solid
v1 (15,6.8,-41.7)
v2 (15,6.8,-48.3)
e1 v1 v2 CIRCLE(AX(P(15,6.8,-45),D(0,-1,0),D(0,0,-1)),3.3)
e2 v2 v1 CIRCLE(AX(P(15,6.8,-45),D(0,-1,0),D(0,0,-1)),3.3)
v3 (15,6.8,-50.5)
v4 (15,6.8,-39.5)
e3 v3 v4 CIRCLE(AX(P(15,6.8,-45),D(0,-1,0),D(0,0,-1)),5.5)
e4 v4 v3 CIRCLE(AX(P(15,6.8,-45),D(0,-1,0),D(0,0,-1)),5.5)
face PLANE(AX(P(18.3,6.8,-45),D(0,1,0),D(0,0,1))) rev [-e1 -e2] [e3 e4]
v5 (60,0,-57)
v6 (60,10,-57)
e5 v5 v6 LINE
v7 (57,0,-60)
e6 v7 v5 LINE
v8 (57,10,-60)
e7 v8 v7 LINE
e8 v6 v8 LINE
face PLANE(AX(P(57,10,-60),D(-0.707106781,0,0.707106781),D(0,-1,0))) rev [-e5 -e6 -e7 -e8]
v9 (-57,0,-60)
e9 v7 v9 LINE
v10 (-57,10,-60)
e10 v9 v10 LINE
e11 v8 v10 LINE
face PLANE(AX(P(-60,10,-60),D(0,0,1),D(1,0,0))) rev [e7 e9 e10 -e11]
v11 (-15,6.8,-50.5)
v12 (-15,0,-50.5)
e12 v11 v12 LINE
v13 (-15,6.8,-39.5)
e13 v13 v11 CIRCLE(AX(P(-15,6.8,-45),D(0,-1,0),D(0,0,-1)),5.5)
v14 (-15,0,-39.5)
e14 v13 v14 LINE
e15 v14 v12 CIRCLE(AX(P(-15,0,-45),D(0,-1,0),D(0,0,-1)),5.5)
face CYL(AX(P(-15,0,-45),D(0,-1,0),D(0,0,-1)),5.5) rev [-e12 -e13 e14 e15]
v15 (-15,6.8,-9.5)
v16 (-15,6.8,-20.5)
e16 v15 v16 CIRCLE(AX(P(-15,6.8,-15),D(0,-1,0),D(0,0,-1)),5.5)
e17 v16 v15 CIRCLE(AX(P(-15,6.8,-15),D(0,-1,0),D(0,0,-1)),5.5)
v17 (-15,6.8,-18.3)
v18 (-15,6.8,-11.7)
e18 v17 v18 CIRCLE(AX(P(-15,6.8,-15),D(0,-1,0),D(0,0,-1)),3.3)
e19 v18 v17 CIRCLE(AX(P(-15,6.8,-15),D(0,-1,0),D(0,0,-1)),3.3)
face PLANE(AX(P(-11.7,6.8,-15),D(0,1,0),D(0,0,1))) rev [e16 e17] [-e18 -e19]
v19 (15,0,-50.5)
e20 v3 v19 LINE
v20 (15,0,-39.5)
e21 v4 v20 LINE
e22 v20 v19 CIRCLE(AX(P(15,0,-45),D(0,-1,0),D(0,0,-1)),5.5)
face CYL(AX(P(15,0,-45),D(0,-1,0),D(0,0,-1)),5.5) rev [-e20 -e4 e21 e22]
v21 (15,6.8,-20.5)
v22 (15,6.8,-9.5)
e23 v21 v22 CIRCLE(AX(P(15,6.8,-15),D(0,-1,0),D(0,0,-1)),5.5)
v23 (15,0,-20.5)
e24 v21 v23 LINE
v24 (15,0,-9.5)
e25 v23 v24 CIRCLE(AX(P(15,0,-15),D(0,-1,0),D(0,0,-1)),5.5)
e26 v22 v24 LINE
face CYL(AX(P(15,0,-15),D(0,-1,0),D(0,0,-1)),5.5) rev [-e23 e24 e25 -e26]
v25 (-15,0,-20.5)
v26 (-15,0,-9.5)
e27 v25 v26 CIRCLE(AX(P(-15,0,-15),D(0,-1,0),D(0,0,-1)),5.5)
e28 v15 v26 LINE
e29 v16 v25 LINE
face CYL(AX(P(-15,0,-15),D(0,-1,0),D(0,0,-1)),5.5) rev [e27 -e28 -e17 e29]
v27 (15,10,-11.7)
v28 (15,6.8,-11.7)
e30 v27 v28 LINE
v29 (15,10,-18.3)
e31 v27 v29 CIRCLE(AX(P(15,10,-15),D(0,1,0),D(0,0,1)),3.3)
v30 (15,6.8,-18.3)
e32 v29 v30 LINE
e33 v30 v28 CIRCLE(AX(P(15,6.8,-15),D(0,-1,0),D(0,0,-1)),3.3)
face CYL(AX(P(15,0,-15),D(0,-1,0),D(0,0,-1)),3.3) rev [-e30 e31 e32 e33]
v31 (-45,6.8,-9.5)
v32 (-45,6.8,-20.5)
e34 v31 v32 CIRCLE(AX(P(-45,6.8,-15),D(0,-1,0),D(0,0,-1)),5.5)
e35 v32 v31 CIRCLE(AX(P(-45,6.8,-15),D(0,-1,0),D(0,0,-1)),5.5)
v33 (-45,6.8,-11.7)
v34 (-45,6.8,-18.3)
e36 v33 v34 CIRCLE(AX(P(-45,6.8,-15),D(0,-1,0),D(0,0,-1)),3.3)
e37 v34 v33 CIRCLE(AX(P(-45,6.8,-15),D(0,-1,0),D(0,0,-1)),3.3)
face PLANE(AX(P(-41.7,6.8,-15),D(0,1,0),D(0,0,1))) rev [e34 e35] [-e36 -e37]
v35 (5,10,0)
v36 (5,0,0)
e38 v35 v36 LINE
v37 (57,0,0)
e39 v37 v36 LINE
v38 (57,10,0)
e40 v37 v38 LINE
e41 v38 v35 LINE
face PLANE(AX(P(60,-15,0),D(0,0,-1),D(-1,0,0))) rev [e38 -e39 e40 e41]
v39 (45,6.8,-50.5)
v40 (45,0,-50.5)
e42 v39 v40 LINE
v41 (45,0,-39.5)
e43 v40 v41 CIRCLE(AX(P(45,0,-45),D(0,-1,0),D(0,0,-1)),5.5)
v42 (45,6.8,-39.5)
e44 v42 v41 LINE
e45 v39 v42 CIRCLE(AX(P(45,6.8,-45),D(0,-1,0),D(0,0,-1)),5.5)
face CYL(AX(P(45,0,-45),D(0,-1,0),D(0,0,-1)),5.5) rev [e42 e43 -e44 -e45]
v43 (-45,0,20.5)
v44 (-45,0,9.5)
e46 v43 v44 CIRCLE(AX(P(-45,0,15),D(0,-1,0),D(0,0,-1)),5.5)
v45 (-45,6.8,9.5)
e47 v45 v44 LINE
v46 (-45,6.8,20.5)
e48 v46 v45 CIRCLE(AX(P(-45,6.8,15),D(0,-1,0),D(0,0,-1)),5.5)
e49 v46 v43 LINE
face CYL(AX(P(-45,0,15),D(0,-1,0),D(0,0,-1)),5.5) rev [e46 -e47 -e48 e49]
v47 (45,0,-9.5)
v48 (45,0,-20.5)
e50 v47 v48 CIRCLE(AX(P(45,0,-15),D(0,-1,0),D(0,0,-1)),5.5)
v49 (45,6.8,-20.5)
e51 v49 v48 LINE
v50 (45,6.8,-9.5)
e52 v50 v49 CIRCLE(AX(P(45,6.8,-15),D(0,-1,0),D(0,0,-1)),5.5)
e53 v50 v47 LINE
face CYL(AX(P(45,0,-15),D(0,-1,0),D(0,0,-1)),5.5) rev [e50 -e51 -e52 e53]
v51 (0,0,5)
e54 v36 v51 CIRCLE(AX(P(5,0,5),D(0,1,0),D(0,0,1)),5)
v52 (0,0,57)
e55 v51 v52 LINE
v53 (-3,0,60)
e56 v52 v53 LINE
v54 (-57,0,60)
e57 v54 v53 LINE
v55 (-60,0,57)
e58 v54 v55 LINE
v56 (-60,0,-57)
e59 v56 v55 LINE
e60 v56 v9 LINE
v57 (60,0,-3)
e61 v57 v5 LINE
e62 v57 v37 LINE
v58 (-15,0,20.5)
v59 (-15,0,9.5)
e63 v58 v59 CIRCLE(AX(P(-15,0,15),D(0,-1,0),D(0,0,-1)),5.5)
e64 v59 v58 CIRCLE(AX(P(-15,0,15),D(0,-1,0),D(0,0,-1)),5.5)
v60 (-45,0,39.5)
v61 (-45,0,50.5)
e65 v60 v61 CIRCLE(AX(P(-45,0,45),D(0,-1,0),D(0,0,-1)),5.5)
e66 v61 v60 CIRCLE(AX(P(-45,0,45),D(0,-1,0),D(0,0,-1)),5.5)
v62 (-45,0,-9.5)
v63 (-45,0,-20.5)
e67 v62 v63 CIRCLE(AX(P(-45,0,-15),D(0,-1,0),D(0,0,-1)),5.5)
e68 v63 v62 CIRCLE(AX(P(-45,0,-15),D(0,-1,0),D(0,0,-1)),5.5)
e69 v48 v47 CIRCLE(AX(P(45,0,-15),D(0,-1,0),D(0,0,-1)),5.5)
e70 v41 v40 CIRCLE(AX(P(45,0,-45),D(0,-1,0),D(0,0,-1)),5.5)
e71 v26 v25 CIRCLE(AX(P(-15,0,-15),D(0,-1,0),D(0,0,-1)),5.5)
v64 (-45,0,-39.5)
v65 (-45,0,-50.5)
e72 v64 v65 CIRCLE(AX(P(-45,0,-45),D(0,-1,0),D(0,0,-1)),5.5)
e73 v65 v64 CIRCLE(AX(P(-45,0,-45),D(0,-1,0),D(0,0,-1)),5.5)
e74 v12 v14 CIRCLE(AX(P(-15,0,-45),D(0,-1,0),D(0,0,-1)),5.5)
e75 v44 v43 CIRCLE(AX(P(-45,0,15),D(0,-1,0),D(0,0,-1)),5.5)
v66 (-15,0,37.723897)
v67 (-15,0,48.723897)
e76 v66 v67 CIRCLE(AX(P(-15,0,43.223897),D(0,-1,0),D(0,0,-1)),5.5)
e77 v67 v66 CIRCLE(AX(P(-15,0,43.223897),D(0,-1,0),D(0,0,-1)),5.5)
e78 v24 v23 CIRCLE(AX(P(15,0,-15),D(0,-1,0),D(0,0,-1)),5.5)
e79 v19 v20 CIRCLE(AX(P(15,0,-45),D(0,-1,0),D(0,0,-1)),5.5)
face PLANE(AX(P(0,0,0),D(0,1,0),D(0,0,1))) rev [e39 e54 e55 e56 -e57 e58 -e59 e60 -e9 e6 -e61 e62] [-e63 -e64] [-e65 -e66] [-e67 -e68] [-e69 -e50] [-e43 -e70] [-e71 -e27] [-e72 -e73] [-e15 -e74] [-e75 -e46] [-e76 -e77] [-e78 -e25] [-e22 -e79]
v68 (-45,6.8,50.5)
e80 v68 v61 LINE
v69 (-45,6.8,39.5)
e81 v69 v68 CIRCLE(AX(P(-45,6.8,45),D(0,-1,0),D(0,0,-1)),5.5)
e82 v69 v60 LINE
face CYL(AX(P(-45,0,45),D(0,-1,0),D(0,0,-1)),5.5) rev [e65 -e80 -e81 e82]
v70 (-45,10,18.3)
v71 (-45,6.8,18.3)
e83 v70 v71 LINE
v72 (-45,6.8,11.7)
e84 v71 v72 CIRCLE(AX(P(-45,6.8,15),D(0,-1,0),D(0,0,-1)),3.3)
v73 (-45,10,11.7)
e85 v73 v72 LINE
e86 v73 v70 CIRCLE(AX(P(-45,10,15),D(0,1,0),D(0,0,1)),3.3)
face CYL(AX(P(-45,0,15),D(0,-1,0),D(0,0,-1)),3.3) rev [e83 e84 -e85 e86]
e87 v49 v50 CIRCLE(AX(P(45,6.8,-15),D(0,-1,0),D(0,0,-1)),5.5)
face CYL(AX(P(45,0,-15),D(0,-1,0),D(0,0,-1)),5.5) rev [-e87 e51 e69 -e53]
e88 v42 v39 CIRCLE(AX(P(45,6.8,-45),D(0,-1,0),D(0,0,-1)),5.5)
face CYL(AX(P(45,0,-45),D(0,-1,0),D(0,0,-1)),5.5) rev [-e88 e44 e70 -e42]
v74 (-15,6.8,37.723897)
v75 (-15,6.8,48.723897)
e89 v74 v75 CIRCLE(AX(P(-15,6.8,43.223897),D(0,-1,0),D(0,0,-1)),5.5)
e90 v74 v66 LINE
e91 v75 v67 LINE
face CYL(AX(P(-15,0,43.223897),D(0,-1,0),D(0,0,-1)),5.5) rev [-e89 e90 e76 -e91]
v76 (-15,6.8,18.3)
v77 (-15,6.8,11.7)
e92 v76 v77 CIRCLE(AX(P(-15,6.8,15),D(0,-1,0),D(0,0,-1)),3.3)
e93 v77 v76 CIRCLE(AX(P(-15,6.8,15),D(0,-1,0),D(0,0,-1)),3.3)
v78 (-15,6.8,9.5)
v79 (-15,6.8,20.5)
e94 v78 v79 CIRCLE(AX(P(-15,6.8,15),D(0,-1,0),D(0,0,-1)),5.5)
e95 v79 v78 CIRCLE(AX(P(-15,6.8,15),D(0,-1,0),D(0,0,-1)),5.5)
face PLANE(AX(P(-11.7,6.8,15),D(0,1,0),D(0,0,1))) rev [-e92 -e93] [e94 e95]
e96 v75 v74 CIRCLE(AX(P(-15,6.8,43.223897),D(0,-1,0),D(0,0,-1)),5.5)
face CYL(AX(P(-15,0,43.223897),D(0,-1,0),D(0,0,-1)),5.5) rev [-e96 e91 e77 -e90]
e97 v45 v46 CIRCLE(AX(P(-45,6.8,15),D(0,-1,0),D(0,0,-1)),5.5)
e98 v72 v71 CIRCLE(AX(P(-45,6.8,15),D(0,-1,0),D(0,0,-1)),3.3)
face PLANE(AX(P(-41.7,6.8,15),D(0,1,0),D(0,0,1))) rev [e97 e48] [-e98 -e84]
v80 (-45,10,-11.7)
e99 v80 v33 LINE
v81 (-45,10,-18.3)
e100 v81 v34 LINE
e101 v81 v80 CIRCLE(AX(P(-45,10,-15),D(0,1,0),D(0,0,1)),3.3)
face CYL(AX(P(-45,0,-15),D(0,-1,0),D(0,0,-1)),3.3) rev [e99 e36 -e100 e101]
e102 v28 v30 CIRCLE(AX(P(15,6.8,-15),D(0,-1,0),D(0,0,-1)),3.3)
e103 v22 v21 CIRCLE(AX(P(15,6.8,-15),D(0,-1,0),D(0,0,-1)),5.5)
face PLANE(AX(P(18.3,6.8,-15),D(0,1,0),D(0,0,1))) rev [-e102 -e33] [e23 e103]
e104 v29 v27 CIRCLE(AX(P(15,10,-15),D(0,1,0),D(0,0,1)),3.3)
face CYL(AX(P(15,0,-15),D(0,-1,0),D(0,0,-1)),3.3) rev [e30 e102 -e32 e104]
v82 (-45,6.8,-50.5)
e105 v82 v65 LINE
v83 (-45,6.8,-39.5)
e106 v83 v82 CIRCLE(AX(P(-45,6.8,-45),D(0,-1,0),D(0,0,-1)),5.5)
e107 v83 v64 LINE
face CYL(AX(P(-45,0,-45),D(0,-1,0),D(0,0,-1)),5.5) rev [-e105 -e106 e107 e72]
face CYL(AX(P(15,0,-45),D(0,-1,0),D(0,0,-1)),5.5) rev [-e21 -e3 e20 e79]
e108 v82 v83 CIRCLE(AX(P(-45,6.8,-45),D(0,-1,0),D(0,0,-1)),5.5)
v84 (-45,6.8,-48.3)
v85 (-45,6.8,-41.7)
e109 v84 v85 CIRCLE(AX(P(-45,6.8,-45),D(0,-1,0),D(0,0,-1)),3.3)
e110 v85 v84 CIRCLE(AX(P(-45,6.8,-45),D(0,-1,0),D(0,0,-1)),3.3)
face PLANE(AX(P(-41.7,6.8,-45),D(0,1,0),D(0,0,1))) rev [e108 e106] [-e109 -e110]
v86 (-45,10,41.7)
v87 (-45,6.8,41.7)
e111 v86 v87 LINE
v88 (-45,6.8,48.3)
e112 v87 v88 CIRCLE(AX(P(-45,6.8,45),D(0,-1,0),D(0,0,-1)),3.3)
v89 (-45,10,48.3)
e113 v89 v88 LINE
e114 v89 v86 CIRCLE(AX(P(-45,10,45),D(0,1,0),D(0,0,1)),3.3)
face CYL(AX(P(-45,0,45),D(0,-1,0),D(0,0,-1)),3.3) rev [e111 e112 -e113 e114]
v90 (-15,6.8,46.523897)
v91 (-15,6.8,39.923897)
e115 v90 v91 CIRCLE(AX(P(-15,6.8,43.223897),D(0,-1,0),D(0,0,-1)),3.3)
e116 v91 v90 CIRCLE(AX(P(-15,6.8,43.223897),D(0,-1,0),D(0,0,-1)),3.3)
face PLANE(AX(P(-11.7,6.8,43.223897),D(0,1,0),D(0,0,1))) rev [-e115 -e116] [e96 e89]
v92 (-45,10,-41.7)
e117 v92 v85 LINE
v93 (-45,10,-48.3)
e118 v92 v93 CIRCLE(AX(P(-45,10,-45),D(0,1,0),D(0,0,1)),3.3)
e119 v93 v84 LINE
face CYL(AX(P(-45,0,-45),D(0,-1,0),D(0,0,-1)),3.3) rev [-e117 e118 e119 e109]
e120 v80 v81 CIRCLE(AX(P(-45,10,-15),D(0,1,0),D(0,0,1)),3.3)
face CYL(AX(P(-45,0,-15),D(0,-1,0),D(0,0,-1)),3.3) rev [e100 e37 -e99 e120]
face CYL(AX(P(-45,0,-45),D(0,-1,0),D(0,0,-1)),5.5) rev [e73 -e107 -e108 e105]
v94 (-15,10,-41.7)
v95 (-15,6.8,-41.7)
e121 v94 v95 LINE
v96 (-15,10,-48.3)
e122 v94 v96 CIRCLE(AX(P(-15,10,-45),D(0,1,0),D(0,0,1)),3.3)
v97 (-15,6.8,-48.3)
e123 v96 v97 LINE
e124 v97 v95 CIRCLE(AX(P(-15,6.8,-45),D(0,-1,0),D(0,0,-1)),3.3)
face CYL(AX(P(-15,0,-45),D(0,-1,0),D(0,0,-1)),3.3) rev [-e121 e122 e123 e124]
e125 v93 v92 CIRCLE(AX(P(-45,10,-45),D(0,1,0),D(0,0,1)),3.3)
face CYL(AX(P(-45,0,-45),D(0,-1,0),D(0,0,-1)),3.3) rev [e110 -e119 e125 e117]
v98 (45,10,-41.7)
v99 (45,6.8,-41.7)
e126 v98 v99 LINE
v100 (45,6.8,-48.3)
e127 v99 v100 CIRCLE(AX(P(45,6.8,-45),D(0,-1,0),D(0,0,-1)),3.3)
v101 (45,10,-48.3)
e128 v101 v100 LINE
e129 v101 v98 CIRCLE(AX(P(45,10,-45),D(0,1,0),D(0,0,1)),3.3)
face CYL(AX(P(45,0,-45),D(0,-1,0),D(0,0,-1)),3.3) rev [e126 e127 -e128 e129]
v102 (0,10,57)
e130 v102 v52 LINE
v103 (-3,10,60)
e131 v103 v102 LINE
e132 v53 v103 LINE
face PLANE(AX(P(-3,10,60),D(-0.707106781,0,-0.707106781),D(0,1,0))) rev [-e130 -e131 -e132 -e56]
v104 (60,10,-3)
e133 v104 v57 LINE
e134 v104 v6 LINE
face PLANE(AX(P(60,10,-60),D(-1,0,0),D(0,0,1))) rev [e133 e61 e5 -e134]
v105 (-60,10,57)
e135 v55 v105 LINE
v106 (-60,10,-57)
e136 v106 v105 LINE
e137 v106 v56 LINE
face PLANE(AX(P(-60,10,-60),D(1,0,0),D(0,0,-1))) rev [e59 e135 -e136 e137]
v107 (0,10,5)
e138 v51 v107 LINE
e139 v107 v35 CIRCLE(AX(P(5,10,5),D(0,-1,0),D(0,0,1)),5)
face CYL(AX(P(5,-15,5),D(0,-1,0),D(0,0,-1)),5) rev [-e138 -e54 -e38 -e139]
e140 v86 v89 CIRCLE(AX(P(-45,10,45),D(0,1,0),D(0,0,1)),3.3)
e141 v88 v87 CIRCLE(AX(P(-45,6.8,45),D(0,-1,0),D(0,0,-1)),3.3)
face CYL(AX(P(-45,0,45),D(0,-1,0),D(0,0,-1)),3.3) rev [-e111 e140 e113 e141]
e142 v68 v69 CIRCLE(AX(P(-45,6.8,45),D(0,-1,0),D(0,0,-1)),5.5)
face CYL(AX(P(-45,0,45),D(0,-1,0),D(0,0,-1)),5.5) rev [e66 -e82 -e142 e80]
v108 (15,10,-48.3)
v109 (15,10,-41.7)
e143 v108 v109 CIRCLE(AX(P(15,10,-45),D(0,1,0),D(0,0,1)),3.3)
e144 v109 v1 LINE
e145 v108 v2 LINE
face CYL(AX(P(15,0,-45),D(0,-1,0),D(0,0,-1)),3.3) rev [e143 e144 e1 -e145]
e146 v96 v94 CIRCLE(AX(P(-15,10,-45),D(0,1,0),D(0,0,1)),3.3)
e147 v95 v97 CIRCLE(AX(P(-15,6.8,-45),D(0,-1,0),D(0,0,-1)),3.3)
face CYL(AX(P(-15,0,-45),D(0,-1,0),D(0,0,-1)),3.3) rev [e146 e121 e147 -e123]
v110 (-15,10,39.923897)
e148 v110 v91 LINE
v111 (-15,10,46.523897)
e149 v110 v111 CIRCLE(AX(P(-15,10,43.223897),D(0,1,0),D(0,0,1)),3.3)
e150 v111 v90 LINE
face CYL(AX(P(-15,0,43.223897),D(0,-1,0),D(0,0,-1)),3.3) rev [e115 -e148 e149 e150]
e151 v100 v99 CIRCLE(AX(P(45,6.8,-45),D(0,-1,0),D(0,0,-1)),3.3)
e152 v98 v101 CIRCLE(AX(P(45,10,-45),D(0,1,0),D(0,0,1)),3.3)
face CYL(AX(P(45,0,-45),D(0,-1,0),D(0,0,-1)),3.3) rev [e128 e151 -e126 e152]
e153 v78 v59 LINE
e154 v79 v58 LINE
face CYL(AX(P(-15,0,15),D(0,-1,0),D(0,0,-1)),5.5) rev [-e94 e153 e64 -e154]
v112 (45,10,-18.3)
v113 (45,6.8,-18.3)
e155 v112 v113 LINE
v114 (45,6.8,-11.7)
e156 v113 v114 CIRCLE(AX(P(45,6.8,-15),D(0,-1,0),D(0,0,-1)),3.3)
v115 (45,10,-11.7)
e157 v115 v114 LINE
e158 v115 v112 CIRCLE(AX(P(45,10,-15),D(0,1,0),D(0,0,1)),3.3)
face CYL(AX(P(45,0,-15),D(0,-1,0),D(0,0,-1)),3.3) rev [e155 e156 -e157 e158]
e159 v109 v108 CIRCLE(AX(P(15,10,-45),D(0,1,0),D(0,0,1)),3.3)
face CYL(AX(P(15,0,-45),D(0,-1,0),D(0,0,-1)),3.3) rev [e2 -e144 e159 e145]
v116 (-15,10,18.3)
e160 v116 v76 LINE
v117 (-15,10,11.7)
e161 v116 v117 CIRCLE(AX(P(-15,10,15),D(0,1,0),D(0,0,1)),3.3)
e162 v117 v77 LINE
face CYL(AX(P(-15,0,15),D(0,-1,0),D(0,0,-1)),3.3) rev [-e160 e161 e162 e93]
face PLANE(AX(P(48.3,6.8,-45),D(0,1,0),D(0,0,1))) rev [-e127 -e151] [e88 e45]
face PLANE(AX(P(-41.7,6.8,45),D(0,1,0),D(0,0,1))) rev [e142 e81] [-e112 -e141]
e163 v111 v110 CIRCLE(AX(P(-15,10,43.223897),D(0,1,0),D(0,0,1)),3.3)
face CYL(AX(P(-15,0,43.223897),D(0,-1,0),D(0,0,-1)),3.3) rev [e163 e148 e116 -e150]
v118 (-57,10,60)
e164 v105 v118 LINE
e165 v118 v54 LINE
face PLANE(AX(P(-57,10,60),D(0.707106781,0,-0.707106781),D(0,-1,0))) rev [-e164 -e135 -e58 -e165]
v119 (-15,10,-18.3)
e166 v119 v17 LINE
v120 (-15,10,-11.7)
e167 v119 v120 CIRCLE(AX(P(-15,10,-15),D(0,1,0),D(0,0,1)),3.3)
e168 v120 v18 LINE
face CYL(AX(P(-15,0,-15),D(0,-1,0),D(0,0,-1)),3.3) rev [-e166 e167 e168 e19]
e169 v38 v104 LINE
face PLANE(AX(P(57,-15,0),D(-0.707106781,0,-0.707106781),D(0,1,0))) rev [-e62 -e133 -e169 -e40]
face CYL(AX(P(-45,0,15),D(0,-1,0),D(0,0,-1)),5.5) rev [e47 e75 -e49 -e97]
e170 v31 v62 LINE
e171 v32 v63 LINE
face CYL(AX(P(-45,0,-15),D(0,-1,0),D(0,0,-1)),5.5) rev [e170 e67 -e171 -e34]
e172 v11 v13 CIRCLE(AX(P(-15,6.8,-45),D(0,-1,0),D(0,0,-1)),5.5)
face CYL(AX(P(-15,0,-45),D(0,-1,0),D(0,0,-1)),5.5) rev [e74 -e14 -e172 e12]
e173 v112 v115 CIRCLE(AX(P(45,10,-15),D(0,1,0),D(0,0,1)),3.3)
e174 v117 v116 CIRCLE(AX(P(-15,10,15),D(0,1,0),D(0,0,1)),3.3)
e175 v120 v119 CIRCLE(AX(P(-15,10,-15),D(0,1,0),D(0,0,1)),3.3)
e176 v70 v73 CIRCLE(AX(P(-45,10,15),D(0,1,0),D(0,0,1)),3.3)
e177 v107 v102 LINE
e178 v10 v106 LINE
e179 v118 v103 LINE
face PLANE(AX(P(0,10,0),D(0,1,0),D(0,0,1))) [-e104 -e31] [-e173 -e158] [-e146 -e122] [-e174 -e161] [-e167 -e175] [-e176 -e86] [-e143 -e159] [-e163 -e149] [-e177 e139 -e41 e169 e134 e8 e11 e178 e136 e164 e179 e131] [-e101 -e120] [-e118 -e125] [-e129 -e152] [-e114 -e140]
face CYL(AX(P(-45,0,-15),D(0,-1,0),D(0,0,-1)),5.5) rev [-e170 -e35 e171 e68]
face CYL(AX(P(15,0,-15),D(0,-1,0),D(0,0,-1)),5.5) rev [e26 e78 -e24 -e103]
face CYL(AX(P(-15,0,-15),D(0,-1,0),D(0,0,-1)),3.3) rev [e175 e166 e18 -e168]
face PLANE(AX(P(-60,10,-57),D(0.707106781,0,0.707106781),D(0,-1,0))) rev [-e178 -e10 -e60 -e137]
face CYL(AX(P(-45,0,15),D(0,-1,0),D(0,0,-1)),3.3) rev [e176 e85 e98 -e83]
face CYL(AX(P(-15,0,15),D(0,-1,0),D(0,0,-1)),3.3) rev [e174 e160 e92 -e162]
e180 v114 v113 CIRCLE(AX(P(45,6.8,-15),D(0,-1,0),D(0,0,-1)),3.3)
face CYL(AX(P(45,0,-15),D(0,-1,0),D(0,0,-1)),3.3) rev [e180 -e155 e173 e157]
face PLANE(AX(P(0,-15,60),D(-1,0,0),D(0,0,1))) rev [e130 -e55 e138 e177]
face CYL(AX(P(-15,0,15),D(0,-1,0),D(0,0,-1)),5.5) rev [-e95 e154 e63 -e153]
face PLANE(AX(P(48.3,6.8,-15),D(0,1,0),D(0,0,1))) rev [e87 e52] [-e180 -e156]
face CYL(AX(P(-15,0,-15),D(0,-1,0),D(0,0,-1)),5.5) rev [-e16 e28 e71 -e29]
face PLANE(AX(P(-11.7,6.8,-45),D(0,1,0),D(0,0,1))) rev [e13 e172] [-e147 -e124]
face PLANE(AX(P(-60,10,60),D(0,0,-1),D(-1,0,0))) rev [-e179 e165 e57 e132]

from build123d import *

# Parameters (mm, degrees)
SKETCH_1_W                = 120
SKETCH_1_H                = 120
EXTRUDE_1_DEPTH           = 10
SKETCH_2_W                = 60
SKETCH_2_H                = 60
CUT_EXTRUDE_1_DEPTH       = 25
CHAMFER_1_SIZE            = 3
FILLET_1_R                = 5
HOLE_WIZARD_1_D           = 6.6
HOLE_WIZARD_1_DEPTH       = 25
HOLE_WIZARD_1_CBORE_D     = 11
HOLE_WIZARD_1_CBORE_DEPTH = 6.8
HOLE_WIZARD_1_TIP         = 1.982840043


with BuildPart() as part:
    # 草图1 → 凸台-拉伸1 (new body)
    with BuildSketch(Plane(origin=(0, 0, 0), x_dir=(1, 0, 0), z_dir=(0, 1, 0))):
        Rectangle(SKETCH_1_W, SKETCH_1_H)
    extrude(amount=EXTRUDE_1_DEPTH)

    # 草图2 → 切除-拉伸1 (cut)
    with BuildSketch(Plane(origin=(0, 10, 0), x_dir=(1, 0, 0), z_dir=(0, 1, 0))):
        with Locations((30, -30)):
            Rectangle(SKETCH_2_W, SKETCH_2_H)
    extrude(amount=-CUT_EXTRUDE_1_DEPTH, mode=Mode.SUBTRACT)

    # 倒角1
    chamfer_1_edges = [part.edges().sort_by_distance(p)[0] for p in [
        (60, 5, 0),
        (0, 5, 60),
        (-60, 5, 60),
        (-60, 5, -60),
        (60, 5, -60),
    ]]
    chamfer(chamfer_1_edges, length=CHAMFER_1_SIZE)

    # 圆角1
    fillet_1_edges = [part.edges().sort_by_distance(p)[0] for p in [
        (0, 5, 0),
    ]]
    fillet(fillet_1_edges, radius=FILLET_1_R)

    # 打孔尺寸(%根据)内六角圆柱头螺钉的类型1
    with Locations(Plane(origin=(0, 0, 0), x_dir=(-1, 0, 0), z_dir=(0, -1, 0))):
        with Locations((45, 45), (45, 15), (15, 45), (15, 15), (-45, 45), (-45, 15), (45, -15), (45, -45), (15, -43.223897071), (15, -15), (-15, 45), (-15, 15)):
            CounterBoreHole(HOLE_WIZARD_1_D / 2, HOLE_WIZARD_1_CBORE_D / 2, HOLE_WIZARD_1_CBORE_DEPTH, depth=HOLE_WIZARD_1_DEPTH)
            with Locations((0, 0, -(HOLE_WIZARD_1_DEPTH + HOLE_WIZARD_1_TIP / 2))):  # 118° drill point
                Cone(0, HOLE_WIZARD_1_D / 2, HOLE_WIZARD_1_TIP, mode=Mode.SUBTRACT)


solid = part.part
